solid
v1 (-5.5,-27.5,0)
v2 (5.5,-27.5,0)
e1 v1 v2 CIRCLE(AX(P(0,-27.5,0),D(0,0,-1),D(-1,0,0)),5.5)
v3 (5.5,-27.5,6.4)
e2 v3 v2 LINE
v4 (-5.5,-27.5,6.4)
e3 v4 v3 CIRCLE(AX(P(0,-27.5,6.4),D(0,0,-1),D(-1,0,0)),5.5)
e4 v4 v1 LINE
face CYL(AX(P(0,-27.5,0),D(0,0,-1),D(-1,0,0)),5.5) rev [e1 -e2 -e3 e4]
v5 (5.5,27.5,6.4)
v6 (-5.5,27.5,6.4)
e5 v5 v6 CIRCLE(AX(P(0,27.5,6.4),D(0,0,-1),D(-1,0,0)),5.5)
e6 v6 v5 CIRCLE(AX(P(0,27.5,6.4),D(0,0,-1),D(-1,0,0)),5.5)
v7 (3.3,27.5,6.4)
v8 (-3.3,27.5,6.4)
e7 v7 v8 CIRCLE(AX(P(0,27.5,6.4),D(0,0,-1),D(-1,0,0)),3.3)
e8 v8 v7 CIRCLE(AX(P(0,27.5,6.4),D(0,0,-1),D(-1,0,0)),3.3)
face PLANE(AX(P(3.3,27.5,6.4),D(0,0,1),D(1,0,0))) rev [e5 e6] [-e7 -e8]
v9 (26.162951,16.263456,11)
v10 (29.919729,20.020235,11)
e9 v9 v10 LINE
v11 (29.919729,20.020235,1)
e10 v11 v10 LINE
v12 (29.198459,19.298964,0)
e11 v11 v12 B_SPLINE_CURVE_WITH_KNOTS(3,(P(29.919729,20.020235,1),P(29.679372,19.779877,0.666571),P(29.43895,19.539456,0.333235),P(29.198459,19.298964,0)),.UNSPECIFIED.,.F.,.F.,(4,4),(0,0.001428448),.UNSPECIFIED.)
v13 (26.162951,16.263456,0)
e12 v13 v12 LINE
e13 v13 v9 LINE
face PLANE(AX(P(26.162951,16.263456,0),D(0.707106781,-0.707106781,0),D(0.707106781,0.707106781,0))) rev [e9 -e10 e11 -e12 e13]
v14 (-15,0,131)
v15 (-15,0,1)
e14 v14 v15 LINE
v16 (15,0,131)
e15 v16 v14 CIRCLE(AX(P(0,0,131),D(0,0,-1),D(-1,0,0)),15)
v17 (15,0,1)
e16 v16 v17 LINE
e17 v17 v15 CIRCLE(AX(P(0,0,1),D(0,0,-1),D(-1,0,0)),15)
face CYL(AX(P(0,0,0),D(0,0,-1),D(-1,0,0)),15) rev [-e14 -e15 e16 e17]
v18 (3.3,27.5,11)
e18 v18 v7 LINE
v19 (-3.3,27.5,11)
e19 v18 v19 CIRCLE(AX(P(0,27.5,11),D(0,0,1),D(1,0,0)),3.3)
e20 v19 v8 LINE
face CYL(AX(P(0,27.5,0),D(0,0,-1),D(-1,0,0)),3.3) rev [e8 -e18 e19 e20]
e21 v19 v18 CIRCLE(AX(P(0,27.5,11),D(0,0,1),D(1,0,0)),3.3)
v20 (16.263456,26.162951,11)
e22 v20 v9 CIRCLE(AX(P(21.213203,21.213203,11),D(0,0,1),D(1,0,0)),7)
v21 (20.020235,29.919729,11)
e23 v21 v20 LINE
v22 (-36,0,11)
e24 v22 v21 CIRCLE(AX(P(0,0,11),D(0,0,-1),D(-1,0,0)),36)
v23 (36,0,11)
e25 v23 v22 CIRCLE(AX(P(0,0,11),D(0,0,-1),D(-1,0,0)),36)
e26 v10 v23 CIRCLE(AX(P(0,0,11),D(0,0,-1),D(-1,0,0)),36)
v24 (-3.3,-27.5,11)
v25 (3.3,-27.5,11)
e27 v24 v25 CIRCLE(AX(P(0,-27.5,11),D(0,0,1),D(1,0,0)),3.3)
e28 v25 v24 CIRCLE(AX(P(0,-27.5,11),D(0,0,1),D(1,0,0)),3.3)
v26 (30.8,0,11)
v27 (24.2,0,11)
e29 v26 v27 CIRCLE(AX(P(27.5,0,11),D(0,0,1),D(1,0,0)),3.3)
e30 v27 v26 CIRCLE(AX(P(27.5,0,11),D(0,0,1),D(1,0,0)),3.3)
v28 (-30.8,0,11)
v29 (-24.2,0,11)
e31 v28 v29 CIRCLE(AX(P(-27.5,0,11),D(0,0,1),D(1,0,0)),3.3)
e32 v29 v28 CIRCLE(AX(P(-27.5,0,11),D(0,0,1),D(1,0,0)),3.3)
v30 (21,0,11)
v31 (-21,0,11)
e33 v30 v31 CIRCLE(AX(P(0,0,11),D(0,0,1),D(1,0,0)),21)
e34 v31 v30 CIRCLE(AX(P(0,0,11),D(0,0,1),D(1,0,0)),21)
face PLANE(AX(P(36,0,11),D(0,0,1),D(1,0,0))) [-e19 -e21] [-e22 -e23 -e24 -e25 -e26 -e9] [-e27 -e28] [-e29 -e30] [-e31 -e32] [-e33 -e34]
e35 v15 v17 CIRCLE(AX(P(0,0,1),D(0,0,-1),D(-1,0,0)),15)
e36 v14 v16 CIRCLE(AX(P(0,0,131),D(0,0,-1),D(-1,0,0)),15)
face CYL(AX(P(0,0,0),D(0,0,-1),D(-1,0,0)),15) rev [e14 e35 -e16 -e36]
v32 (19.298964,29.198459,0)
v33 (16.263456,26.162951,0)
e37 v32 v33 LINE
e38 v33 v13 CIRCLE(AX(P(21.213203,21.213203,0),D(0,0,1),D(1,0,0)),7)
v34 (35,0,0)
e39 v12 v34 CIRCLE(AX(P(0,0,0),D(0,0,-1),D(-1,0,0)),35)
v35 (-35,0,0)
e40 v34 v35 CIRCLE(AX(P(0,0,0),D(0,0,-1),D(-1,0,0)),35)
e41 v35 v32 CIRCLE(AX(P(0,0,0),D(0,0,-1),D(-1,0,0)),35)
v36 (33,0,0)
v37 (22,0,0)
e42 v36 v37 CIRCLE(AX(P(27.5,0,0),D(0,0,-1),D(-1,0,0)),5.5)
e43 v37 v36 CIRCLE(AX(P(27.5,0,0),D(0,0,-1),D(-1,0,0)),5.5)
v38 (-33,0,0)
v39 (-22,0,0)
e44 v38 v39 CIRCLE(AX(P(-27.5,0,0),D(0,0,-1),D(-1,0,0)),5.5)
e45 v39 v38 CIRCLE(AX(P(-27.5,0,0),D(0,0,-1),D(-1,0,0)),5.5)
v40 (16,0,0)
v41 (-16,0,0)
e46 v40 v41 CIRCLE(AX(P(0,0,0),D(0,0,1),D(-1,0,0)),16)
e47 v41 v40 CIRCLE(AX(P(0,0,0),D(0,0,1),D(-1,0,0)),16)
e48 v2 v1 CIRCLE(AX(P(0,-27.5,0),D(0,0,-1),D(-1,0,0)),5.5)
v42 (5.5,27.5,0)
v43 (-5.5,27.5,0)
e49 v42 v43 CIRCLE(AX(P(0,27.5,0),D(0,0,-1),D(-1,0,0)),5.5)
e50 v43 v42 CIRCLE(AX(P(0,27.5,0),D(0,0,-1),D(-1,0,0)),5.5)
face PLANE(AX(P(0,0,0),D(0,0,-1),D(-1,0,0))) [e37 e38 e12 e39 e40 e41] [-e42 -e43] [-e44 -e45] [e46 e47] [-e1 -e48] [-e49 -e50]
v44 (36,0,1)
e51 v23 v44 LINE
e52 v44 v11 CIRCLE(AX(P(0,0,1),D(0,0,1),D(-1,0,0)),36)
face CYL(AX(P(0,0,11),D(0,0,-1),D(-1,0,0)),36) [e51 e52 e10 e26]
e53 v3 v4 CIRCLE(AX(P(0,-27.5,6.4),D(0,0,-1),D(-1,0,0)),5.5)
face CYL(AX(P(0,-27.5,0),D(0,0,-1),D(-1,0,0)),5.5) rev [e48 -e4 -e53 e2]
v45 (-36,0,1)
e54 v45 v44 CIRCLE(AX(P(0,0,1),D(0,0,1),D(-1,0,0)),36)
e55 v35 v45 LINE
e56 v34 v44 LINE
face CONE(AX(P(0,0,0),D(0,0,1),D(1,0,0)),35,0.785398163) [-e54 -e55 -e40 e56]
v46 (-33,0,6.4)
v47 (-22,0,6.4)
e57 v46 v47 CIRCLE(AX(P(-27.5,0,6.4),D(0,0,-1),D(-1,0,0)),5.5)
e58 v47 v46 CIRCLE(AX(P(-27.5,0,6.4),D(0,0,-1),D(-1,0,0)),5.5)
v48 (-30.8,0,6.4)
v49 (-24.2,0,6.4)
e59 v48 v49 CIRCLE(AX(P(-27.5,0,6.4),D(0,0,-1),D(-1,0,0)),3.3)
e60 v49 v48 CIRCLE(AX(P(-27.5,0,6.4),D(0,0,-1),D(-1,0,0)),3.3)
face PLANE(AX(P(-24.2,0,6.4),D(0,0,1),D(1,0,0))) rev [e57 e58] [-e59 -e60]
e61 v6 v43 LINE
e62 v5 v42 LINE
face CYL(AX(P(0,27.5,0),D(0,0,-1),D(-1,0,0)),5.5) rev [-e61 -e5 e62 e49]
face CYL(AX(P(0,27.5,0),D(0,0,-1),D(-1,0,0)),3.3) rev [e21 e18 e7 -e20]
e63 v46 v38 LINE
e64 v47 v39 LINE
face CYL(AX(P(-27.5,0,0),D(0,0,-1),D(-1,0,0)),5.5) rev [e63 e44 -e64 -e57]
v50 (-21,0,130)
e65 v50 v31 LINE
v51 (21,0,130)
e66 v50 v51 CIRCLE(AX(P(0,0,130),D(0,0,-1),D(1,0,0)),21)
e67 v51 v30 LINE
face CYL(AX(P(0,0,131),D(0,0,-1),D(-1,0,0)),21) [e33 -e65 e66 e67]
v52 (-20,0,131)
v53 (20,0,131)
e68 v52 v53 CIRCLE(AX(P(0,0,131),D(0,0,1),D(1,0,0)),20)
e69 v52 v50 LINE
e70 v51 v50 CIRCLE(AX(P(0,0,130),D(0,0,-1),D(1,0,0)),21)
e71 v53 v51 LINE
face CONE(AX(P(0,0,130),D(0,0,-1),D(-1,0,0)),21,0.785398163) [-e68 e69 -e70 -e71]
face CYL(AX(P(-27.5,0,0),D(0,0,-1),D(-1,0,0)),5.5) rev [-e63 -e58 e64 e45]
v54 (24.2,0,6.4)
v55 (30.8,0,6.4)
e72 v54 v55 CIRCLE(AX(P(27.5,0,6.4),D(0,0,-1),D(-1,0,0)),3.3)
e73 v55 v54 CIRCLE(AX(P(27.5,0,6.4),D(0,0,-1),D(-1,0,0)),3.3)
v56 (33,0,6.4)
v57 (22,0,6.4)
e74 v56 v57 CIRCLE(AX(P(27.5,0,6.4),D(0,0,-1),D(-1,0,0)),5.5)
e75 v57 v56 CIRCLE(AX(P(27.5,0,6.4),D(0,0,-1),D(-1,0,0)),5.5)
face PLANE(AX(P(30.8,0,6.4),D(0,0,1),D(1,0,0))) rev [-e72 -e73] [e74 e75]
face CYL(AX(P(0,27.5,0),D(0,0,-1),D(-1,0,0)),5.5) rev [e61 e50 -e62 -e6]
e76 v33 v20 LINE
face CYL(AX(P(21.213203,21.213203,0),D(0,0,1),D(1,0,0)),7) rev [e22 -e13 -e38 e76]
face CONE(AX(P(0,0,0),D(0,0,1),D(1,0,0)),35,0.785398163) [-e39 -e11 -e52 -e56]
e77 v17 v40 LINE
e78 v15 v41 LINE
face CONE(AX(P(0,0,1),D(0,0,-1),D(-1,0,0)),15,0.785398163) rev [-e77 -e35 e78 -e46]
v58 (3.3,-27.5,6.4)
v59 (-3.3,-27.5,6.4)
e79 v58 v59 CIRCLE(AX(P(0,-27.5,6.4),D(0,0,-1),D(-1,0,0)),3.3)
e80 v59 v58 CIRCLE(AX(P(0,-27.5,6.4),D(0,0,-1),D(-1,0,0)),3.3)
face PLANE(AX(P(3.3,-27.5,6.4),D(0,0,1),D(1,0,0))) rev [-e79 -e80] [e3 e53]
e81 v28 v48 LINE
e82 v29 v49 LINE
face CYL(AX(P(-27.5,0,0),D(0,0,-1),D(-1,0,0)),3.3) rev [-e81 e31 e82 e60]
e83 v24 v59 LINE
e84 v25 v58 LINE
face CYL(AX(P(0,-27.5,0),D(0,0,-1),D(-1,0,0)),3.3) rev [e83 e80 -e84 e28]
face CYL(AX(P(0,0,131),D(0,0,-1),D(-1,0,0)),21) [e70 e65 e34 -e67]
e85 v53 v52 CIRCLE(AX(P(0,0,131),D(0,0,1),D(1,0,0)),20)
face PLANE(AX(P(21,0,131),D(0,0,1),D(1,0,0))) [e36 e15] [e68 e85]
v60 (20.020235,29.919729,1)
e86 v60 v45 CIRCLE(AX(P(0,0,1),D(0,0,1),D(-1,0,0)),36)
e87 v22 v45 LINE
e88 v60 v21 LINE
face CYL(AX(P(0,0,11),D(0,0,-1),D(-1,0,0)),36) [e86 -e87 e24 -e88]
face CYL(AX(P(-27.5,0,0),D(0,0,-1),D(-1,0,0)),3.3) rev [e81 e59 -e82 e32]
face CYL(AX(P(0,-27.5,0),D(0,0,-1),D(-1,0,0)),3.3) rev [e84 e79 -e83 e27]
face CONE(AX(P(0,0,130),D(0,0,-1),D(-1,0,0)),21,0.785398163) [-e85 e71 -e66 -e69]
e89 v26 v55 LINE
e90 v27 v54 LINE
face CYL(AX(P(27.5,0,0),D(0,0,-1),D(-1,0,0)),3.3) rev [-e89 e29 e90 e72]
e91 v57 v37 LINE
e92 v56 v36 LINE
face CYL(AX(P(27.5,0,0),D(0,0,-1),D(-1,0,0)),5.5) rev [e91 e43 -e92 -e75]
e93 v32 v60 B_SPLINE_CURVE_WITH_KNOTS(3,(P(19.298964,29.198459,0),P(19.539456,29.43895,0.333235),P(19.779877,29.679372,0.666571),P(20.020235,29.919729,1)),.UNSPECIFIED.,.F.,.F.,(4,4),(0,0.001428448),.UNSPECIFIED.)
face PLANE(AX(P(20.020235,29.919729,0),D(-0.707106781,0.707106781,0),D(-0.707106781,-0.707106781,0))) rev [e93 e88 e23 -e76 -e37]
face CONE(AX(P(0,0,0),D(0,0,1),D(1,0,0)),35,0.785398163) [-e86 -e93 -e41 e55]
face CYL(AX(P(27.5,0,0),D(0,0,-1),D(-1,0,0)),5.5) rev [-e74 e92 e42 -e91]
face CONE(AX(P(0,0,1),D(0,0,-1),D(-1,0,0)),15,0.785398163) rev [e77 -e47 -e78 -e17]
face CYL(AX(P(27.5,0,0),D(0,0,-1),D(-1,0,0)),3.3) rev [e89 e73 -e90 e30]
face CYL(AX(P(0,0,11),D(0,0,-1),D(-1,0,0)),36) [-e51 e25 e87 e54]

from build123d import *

# Parameters (mm, degrees)
SKETCH_1_W                   = 36
SKETCH_1_H                   = 11
CUT_EXTRUDE_1_DEPTH          = 53.086466572
SKETCH_3_W                   = 21
SKETCH_3_H                   = 120
HOLE_WIZARD_M27_1_D          = 30
HOLE_WIZARD_M6_1_D           = 6.6
HOLE_WIZARD_M6_1_DEPTH       = 131
HOLE_WIZARD_M6_1_CBORE_D     = 11
HOLE_WIZARD_M6_1_CBORE_DEPTH = 6.4
CHAMFER_1_SIZE               = 1


with BuildPart() as part:
    # 草图1 → 旋转1 (revolve)
    with BuildSketch(Plane.XZ, mode=Mode.PRIVATE) as revolve_1_sk:
        with Locations((18, 5.5)):
            Rectangle(SKETCH_1_W, SKETCH_1_H)
    revolve(revolve_1_sk.sketch.rotate(Axis((0, 0, 11), (0, 0, -1)), 180), axis=Axis((0, 0, 11), (0, 0, -1)))

    # 草图2 → 切除-拉伸1 (cut, through all)
    with BuildSketch(Plane.XY.offset(11)):
        with BuildLine():
            Line((20.02023451, 29.919729447), (16.263455967, 26.162950904))
            ThreePointArc((16.263455967, 26.162950904), (16.263455967, 16.263455967), (26.162950904, 16.263455967))
            Line((26.162950904, 16.263455967), (29.919729447, 20.02023451))
            ThreePointArc((29.919729447, 20.02023451), (25.455844123, 25.455844123), (20.02023451, 29.919729447))
        make_face()
    extrude(amount=-CUT_EXTRUDE_1_DEPTH, mode=Mode.SUBTRACT)

    # 草图3 → 旋转2 (revolve)
    with BuildSketch(Plane.XZ, mode=Mode.PRIVATE) as revolve_2_sk:
        with Locations((10.5, 71)):
            Rectangle(SKETCH_3_W, SKETCH_3_H)
    revolve(revolve_2_sk.sketch.rotate(Axis((0, 0, 131), (0, 0, -1)), 180), axis=Axis((0, 0, 131), (0, 0, -1)))

    # M27 间隙孔1 (through all)
    with Locations(Plane(origin=(0, 0, 0), x_dir=(-1, 0, 0), z_dir=(0, 0, -1))):
        with Locations((0, 0)):
            Hole(HOLE_WIZARD_M27_1_D / 2)

    # M6 六角头螺栓的柱形沉头孔1
    with Locations(Plane(origin=(0, 0, 0), x_dir=(-1, 0, 0), z_dir=(0, 0, -1))):
        with Locations((0, 27.5), (27.5, 0), (0, -27.5), (-27.5, 0)):
            CounterBoreHole(HOLE_WIZARD_M6_1_D / 2, HOLE_WIZARD_M6_1_CBORE_D / 2, HOLE_WIZARD_M6_1_CBORE_DEPTH, depth=HOLE_WIZARD_M6_1_DEPTH)

    # 倒角1
    chamfer_1_edges = [part.edges().sort_by_distance(p)[0] for p in [
        (-25.455844123, -25.455844123, 0),
        (21, 0, 131),
        (-15, 0, 0),
    ]]
    chamfer(chamfer_1_edges, length=CHAMFER_1_SIZE)


solid = part.part
